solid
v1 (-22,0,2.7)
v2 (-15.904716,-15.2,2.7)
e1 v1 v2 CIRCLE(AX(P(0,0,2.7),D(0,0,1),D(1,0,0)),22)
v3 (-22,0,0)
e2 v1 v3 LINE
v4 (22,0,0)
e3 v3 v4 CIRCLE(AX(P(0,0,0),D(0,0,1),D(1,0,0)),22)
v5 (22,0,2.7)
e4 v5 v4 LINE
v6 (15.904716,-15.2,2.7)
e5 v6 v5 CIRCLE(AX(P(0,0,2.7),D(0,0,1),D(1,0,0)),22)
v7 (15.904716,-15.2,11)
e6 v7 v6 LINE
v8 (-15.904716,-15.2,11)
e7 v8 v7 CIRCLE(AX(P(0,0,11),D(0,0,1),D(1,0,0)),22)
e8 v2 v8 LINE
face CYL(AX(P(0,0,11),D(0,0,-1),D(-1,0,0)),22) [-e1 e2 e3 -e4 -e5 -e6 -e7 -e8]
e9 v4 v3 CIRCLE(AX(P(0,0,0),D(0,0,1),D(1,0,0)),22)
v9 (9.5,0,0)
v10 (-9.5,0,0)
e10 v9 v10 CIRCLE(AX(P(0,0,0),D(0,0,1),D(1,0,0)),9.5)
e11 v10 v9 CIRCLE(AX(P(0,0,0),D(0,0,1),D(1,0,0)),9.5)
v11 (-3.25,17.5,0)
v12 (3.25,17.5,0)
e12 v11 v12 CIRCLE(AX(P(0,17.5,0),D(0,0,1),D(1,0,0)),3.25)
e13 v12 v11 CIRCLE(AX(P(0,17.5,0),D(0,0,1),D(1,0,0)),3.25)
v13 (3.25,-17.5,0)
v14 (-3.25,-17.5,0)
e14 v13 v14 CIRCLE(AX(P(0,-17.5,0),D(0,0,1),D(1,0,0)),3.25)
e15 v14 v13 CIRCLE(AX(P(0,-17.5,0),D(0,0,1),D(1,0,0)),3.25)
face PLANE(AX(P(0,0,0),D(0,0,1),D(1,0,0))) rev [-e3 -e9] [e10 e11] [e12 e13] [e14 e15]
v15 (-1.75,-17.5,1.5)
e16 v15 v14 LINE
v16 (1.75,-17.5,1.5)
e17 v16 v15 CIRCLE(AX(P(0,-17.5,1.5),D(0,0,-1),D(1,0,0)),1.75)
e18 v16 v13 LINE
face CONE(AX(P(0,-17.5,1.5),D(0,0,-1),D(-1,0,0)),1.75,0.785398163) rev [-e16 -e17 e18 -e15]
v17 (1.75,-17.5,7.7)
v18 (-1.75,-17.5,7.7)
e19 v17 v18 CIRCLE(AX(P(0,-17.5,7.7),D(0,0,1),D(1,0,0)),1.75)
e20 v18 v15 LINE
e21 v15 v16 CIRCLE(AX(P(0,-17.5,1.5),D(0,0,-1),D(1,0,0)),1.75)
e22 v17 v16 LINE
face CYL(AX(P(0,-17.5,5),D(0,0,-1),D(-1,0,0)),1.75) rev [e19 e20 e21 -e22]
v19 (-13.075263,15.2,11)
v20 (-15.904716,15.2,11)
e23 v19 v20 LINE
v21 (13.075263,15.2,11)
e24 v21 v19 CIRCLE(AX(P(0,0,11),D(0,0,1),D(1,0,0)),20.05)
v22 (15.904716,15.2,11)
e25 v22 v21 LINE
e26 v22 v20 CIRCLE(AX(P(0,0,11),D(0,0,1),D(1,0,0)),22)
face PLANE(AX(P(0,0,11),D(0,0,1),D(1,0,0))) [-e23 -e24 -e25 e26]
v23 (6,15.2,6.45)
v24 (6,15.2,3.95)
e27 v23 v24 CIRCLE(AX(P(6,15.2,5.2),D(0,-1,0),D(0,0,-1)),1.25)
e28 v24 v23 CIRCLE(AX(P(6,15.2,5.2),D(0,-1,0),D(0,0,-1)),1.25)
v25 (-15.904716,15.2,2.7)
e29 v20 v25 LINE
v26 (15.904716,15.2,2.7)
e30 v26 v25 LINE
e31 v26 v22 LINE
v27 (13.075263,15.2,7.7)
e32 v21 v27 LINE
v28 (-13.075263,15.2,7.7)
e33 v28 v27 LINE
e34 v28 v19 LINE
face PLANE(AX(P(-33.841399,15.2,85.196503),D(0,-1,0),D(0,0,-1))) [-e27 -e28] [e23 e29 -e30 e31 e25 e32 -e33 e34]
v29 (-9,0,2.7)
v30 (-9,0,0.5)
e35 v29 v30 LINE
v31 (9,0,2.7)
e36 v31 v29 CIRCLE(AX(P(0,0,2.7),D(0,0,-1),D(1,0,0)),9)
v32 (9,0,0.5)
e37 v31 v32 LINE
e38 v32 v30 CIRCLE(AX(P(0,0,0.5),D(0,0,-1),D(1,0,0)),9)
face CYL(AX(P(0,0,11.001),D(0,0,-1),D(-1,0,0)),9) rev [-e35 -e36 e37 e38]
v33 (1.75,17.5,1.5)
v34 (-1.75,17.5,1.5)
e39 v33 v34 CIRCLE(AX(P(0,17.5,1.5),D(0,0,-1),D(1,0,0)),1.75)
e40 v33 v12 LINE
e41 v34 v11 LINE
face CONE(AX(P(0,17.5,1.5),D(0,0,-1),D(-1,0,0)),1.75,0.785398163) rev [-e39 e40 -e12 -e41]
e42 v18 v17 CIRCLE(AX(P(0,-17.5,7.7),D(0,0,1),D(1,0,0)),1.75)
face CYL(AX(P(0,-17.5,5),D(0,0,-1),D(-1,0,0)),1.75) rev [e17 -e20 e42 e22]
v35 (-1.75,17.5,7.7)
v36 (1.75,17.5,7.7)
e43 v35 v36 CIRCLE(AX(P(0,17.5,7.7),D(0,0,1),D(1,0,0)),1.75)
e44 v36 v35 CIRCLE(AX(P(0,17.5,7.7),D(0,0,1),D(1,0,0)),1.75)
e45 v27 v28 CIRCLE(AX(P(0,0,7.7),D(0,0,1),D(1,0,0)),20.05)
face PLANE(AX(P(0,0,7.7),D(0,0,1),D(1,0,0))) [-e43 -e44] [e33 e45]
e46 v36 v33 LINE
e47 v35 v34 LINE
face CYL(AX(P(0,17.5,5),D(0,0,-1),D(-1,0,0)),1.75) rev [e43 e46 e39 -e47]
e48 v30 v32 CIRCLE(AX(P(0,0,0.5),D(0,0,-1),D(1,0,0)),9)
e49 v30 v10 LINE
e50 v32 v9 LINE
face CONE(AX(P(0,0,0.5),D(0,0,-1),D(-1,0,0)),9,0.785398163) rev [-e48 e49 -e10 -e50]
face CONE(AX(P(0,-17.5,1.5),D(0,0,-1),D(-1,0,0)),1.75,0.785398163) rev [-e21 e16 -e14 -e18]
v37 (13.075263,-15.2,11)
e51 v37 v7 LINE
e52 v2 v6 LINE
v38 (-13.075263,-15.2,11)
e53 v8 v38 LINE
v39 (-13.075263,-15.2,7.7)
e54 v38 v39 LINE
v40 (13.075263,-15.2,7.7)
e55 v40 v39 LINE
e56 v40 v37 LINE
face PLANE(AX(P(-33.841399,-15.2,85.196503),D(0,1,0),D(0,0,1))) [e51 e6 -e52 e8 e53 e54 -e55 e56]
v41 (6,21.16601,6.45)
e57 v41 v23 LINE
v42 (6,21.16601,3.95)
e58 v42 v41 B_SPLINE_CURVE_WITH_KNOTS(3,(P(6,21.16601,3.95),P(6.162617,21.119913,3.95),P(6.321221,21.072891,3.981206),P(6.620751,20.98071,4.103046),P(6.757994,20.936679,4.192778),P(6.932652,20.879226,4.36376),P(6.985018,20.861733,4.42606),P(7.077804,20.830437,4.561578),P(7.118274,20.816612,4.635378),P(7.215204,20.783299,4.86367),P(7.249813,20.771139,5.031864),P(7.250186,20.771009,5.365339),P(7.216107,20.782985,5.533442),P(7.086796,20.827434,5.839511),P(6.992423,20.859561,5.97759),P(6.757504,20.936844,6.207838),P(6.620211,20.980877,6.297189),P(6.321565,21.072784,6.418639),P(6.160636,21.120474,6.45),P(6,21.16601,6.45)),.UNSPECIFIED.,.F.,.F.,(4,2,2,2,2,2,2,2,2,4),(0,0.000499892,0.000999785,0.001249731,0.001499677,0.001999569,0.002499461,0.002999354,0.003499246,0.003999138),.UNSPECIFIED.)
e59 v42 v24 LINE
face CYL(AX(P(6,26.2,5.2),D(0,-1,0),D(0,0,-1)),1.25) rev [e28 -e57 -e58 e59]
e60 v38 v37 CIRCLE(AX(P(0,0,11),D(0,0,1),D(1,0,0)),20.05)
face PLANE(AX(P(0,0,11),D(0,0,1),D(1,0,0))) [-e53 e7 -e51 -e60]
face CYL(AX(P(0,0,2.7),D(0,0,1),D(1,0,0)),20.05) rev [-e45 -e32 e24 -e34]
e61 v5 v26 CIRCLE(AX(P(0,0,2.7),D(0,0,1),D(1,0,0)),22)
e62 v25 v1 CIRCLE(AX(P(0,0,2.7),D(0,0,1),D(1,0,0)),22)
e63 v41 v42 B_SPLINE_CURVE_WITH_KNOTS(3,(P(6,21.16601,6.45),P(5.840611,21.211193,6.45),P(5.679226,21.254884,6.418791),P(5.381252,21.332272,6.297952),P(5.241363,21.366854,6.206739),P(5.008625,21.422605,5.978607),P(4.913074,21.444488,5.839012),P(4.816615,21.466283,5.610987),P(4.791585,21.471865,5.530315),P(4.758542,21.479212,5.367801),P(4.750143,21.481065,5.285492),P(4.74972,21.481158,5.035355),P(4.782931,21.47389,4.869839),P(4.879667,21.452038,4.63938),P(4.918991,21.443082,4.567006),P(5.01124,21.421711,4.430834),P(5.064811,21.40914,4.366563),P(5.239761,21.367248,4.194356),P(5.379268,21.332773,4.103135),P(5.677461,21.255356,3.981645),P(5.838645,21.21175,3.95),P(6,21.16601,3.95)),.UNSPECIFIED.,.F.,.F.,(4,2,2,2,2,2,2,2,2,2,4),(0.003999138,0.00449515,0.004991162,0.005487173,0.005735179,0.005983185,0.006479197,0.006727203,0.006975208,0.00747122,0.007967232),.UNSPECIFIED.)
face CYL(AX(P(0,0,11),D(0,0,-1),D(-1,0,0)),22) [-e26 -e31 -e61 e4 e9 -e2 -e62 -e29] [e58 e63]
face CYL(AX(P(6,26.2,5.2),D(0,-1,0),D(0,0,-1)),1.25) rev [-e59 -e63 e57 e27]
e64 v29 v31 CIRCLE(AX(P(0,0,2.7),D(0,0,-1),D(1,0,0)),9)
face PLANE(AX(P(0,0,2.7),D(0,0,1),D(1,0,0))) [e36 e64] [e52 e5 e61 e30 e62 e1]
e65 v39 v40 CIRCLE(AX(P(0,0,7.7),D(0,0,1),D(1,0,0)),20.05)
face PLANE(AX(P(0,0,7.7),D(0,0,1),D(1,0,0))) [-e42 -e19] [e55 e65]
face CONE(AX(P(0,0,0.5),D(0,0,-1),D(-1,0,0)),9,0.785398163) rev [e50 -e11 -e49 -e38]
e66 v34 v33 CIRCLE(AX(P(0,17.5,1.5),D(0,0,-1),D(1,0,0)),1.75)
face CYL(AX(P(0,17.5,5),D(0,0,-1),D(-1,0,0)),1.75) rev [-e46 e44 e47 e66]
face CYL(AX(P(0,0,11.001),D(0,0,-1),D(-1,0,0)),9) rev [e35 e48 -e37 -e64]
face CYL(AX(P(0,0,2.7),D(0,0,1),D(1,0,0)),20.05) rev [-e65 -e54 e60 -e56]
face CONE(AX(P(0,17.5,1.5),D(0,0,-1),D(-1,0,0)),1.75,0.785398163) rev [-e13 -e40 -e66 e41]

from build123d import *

# Parameters (mm, degrees)
SKETCH1_R           = 22
BOSS_EXTRUDE1_DEPTH = 11
SKETCH2_R           = 20.05
CUT_EXTRUDE1_DEPTH  = 8.3
SKETCH3_W           = 67.682797152
SKETCH3_H           = 30.4
CUT_EXTRUDE2_DEPTH  = 8.3
SKETCH4_R           = 1.75
CUT_EXTRUDE3_DEPTH  = 5
CIRPATTERN1_COUNT   = 2
CUT_EXTRUDE4_REACH  = 35
SKETCH5_R           = 9
CHAMFER1_SIZE       = 1.5
CHAMFER2_SIZE       = 0.5
SKETCH6_OUTSIDE_W   = 58.638
SKETCH6_OUTSIDE_H   = 58.638
SKETCH6_OUTSIDE_W_2 = 90.952157774
SKETCH6_OUTSIDE_H_2 = 47
CUT_EXTRUDE5_DEPTH  = 8.3
BOSS_EXTRUDE2_START = 5
SKETCH7_R           = 1.75
BOSS_EXTRUDE2_DEPTH = 5
SKETCH8_R           = 1.25
CUT_EXTRUDE6_DEPTH  = 11


with BuildPart() as part:
    # Sketch1 → Boss-Extrude1 (new body)
    with BuildSketch(Plane.XY):
        Circle(SKETCH1_R)
    extrude(amount=BOSS_EXTRUDE1_DEPTH)

    # Sketch2 → Cut-Extrude1 (cut)
    with BuildSketch(Plane.XY.offset(11)):
        Circle(SKETCH2_R)
    extrude(amount=-CUT_EXTRUDE1_DEPTH, mode=Mode.SUBTRACT)

    # Sketch3 → Cut-Extrude2 (cut)
    with BuildSketch(Plane.XY.offset(2.7)):
        Rectangle(SKETCH3_W, SKETCH3_H)
    extrude(amount=CUT_EXTRUDE2_DEPTH, mode=Mode.SUBTRACT)

    # Sketch4 → Cut-Extrude3 (cut)
    with BuildSketch(Plane(origin=(0, 0, 0), x_dir=(-1, 0, 0), z_dir=(0, 0, -1))):
        with Locations((0, 17.5)):
            Circle(SKETCH4_R)
    cut_extrude3 = extrude(amount=-CUT_EXTRUDE3_DEPTH, mode=Mode.SUBTRACT)

    # CirPattern1: Cut-Extrude3 ×2 about axis
    cirpattern1_axis = Axis((0, 0, 0), (0, 0, 1))
    for i in range(1, CIRPATTERN1_COUNT):
        add(cut_extrude3.rotate(cirpattern1_axis, i * 360 / CIRPATTERN1_COUNT), mode=Mode.SUBTRACT)

    # Sketch5 → Cut-Extrude4 (cut, up to next)
    with BuildSketch(Plane(origin=(0, 0, 0), x_dir=(-1, 0, 0), z_dir=(0, 0, -1)), mode=Mode.PRIVATE) as cut_extrude4_sk1:
        Circle(SKETCH5_R)
    cut_extrude4_tool1 = extrude(cut_extrude4_sk1.sketch, amount=-CUT_EXTRUDE4_REACH, mode=Mode.PRIVATE) & part.part
    add(cut_extrude4_tool1.solids().sort_by_distance((0, 0, 0))[0], mode=Mode.SUBTRACT)

    # Chamfer1
    chamfer1_edges = [part.edges().sort_by_distance(p)[0] for p in [
        (1.75, 17.5, 0),
        (-1.75, -17.5, 0),
    ]]
    chamfer(chamfer1_edges, length=CHAMFER1_SIZE)

    # Chamfer2
    chamfer2_edges = [part.edges().sort_by_distance(p)[0] for p in [
        (9, 0, 0),
    ]]
    chamfer(chamfer2_edges, length=CHAMFER2_SIZE)

    # Sketch6 outside → Cut-Extrude5 (cut)
    with BuildSketch(Plane.XY.offset(11)):
        Rectangle(SKETCH6_OUTSIDE_W, SKETCH6_OUTSIDE_H)
        Rectangle(SKETCH6_OUTSIDE_W_2, SKETCH6_OUTSIDE_H_2, mode=Mode.SUBTRACT)
    extrude(amount=-CUT_EXTRUDE5_DEPTH, mode=Mode.SUBTRACT)

    # Sketch7 → Boss-Extrude2 (add)
    # profile 1 of 2: a face of its own
    with BuildSketch(Plane.XY.offset(2.7).offset(BOSS_EXTRUDE2_START)):
        with BuildLine():
            Line((-13.075262904, 15.2), (13.075262904, 15.2))
            ThreePointArc((13.075262904, 15.2), (0, 20.05), (-13.075262904, 15.2))
        make_face()
        with Locations((0, 17.5)):
            Circle(SKETCH7_R, mode=Mode.SUBTRACT)
    # profile 2 of 2: a face of its own
    with BuildSketch(Plane.XY.offset(2.7).offset(BOSS_EXTRUDE2_START)):
        with BuildLine():
            Line((-13.075262904, -15.2), (13.075262904, -15.2))
            ThreePointArc((13.075262904, -15.2), (0, -20.05), (-13.075262904, -15.2))
        make_face()
        with Locations((0, -17.5)):
            Circle(SKETCH7_R, mode=Mode.SUBTRACT)
    extrude(amount=-BOSS_EXTRUDE2_DEPTH)

    # Sketch8 → Cut-Extrude6 (cut)
    with BuildSketch(Plane.XZ.offset(-15.2)):
        with Locations(Location((6, 5.2, 0), (0, 0, 270))):
            Circle(SKETCH8_R)
    extrude(amount=-CUT_EXTRUDE6_DEPTH, mode=Mode.SUBTRACT)


solid = part.part
